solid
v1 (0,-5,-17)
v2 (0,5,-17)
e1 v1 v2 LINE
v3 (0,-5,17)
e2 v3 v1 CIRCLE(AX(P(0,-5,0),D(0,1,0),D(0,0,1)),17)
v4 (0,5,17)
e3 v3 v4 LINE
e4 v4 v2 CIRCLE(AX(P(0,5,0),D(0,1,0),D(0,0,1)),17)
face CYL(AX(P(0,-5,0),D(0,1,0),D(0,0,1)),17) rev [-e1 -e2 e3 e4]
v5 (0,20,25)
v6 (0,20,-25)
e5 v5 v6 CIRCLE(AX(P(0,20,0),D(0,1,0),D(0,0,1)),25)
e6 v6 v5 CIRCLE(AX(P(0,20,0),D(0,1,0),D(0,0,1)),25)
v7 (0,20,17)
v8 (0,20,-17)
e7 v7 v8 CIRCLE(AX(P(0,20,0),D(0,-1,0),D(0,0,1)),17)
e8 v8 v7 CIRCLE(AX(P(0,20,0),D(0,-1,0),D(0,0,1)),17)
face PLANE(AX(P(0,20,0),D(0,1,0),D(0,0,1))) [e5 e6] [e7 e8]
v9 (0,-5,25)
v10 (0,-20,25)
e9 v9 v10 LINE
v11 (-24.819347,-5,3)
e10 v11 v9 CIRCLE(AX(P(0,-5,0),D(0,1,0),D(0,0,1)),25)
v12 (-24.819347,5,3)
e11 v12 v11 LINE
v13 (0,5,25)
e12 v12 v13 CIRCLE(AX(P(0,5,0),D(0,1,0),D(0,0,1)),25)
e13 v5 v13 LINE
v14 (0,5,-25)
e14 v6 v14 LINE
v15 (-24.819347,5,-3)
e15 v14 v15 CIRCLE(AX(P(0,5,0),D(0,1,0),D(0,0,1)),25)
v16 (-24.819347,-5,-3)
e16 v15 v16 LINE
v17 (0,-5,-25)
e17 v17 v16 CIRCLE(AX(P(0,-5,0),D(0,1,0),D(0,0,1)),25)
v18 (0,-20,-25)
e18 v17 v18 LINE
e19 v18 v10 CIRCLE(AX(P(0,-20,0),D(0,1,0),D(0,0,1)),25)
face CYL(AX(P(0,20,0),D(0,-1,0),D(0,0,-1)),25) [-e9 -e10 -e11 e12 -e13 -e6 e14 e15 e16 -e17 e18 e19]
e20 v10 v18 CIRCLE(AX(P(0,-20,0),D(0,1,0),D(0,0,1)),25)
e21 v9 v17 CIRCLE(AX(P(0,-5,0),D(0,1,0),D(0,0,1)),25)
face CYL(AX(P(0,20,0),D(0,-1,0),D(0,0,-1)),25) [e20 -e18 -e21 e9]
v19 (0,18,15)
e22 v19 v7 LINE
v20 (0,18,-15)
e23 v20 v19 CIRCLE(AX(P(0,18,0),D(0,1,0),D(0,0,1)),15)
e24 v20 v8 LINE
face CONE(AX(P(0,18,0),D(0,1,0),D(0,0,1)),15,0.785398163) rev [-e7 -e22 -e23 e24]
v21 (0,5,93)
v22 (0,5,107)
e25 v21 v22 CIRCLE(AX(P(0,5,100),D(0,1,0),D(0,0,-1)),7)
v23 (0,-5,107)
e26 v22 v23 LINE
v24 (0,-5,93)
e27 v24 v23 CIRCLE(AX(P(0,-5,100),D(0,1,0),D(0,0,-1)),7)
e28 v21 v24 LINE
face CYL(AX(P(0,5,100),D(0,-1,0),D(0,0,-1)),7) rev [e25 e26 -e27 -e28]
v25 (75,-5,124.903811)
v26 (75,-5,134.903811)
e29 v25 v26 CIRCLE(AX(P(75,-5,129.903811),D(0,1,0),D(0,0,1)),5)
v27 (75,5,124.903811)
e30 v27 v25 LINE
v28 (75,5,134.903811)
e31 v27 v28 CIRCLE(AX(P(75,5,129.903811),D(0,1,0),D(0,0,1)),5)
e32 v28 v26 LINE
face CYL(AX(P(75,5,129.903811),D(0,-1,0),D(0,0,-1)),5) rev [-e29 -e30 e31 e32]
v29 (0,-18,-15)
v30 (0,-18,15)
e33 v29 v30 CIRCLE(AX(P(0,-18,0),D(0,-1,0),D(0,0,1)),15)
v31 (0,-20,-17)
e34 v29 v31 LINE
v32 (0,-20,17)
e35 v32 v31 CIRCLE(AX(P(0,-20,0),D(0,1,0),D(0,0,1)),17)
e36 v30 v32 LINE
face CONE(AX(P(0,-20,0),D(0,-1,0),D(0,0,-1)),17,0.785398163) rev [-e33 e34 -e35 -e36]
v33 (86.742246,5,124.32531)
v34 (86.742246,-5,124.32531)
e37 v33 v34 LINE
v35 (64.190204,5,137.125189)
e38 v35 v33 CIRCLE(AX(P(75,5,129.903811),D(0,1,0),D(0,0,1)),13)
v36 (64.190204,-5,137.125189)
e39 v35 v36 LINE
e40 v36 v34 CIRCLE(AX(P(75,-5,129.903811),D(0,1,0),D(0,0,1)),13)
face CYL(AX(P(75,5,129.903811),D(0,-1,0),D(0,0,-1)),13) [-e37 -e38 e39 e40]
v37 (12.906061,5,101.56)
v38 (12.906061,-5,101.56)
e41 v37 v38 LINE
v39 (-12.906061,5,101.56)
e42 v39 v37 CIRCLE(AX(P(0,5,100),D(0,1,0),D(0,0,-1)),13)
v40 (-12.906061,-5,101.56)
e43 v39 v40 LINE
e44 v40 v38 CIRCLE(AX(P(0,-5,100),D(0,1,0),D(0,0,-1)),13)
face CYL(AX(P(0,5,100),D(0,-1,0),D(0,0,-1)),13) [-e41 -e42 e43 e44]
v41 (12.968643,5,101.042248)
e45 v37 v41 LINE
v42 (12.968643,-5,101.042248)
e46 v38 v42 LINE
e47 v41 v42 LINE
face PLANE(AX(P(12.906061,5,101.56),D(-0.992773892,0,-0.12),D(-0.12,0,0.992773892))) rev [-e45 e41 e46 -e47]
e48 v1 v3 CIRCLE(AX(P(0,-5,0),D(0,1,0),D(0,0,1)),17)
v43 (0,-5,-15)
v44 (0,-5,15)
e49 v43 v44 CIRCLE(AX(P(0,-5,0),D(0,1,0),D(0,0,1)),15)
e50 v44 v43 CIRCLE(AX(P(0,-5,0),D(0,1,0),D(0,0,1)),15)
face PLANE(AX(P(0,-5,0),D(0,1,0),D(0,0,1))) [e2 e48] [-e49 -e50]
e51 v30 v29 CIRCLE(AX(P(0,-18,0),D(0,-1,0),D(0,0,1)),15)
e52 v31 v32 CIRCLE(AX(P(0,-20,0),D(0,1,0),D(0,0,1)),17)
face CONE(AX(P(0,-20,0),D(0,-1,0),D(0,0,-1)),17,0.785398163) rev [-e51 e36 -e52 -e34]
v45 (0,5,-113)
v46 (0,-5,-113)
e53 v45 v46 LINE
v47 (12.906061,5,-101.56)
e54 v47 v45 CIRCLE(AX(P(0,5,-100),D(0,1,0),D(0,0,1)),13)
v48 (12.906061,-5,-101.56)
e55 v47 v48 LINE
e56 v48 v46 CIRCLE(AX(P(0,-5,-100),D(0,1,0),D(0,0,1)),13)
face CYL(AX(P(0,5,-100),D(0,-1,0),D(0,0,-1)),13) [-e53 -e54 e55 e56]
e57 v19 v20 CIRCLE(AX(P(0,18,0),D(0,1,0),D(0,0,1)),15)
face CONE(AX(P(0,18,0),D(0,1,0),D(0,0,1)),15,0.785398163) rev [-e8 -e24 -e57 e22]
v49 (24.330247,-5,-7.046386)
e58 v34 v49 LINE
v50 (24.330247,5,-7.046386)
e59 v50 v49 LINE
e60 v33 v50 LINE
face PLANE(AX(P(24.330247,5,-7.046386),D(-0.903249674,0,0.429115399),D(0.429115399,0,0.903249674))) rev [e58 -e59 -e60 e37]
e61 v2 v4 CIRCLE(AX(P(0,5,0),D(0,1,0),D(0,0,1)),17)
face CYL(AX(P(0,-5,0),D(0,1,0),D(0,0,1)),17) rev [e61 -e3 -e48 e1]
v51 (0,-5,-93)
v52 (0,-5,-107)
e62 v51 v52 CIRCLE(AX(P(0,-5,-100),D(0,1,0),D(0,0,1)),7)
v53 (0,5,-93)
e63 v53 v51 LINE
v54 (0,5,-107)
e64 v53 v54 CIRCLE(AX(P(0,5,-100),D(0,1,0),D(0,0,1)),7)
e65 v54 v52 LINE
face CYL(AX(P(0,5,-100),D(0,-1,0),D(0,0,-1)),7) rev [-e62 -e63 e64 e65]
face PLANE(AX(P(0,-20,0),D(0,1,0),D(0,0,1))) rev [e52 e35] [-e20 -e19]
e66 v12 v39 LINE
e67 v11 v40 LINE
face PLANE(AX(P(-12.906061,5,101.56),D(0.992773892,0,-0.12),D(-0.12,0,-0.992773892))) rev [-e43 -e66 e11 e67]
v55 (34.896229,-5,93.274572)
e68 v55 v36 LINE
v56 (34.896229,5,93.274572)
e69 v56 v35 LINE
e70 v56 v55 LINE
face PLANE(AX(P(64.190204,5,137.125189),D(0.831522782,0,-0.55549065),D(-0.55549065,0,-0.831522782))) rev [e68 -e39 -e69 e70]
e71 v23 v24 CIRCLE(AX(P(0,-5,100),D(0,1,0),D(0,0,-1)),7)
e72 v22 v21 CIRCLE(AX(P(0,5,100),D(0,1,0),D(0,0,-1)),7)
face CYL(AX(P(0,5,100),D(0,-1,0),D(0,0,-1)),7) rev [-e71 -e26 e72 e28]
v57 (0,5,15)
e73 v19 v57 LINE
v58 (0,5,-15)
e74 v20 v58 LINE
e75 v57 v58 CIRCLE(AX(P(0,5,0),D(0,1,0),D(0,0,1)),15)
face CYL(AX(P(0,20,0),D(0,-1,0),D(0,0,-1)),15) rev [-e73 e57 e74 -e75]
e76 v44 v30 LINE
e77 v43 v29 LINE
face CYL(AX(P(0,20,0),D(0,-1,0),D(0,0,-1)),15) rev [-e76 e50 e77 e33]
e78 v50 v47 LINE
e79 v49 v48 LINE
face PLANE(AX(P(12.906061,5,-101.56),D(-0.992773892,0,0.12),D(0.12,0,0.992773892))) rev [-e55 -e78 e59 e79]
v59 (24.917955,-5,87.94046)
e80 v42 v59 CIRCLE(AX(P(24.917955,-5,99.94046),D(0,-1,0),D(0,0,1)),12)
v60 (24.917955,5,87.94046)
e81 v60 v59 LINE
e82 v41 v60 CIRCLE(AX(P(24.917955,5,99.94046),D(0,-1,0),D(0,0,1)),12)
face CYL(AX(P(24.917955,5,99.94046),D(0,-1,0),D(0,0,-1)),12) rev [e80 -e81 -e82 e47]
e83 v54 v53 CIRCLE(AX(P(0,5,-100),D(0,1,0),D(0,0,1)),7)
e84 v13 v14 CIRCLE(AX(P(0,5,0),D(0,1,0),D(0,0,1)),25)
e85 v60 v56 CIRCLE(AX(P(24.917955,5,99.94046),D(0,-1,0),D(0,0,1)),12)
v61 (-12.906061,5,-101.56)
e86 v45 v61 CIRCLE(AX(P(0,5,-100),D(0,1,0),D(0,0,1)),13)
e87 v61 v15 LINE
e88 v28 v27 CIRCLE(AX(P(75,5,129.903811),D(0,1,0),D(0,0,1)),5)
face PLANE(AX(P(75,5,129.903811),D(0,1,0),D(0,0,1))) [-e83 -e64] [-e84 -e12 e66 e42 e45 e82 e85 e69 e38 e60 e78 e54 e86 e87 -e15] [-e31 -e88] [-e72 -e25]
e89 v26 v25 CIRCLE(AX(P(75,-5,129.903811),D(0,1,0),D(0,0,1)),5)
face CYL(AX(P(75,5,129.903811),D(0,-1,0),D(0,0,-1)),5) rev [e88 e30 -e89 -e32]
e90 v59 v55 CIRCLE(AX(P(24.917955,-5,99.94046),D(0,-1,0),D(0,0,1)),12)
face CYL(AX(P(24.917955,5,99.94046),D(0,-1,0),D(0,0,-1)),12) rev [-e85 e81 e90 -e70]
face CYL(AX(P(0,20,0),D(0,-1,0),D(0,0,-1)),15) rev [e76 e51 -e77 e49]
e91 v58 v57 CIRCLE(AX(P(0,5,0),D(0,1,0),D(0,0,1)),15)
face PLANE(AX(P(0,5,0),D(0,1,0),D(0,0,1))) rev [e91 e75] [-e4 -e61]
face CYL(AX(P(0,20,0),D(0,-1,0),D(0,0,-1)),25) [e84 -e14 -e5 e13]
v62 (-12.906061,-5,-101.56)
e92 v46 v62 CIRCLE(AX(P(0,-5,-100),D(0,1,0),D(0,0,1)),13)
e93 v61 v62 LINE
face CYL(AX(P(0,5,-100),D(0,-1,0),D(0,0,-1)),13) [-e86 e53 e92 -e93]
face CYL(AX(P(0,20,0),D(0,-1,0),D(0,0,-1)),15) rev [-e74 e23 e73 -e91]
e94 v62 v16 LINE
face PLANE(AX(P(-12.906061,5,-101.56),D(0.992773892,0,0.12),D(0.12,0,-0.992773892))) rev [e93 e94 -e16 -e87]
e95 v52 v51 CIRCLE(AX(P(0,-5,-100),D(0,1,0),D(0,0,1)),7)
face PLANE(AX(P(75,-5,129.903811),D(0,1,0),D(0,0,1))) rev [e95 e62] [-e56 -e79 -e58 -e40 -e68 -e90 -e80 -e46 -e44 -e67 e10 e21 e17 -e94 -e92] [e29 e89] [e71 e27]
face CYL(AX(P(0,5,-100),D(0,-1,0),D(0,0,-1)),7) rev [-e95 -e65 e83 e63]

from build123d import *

# Parameters (mm, degrees)
SKETCH_1_R          = 25
SKETCH_1_R_2        = 15
EXTRUDE_1_DEPTH     = 20
SKETCH_2_R          = 15
SKETCH_2_R_2        = 7
SKETCH_2_R_3        = 5
EXTRUDE_2_DEPTH     = 5
CHAMFER_1_SIZE      = 2
SKETCH_3_R          = 17
CUT_EXTRUDE_1_DEPTH = 10


with BuildPart() as part:
    # 草图1 → 凸台-拉伸1 (new, symmetric)
    with BuildSketch(Plane(origin=(0, 0, 0), x_dir=(1, 0, 0), z_dir=(0, 1, 0))):
        with Locations(Location((0, 0, 0), (0, 0, 270))):
            Circle(SKETCH_1_R)
        with Locations(Location((0, 0, 0), (0, 0, 270))):
            Circle(SKETCH_1_R_2, mode=Mode.SUBTRACT)
    extrude(amount=EXTRUDE_1_DEPTH, both=True)

    # 草图2 → 凸台-拉伸2 (add, symmetric)
    with BuildSketch(Plane(origin=(0, 0, 0), x_dir=(1, 0, 0), z_dir=(0, 1, 0))):
        with BuildLine():
            Line((-12.906060592, 101.56), (-24.819347292, 3))
            ThreePointArc((-24.819347292, 3), (-25, 0), (-24.819347292, -3))
            Line((-24.819347292, -3), (-12.906060592, -101.56))
            ThreePointArc((-12.906060592, -101.56), (0, -113), (12.906060592, -101.56))
            Line((12.906060592, -101.56), (12.968643035, -101.042248202))
            ThreePointArc((12.968643035, -101.042248202), (20.91103038, -88.629202002), (34.896228635, -93.274572004))
            Line((34.896228635, -93.274572004), (64.19020383, -137.125189021))
            ThreePointArc((64.19020383, -137.125189021), (81.416898698, -141.209712173), (86.742245765, -124.325310375))
            Line((86.742245765, -124.325310375), (24.330246726, 7.046385599))
            Line((24.330246726, 7.046385599), (12.906060592, 101.56))
            ThreePointArc((12.906060592, 101.56), (0, 113), (-12.906060592, 101.56))
        make_face()
        with Locations(Location((0, 0, 0), (0, 0, 270))):
            Circle(SKETCH_2_R, mode=Mode.SUBTRACT)
        with Locations(Location((0, 100, 0), (0, 0, 270))):
            Circle(SKETCH_2_R_2, mode=Mode.SUBTRACT)
        with Locations(Location((0, -100, 0), (0, 0, 90))):
            Circle(SKETCH_2_R_2, mode=Mode.SUBTRACT)
        with Locations(Location((75, -129.903810568, 0), (0, 0, 270))):
            Circle(SKETCH_2_R_3, mode=Mode.SUBTRACT)
    extrude(amount=EXTRUDE_2_DEPTH, both=True)

    # 倒角1
    chamfer_1_edges = [part.edges().sort_by_distance(p)[0] for p in [
        (0, -20, -15),
        (0, 20, -15),
    ]]
    chamfer(chamfer_1_edges, length=CHAMFER_1_SIZE)

    # 草图3 → 切除-拉伸1 (cut)
    with BuildSketch(Plane(origin=(0, 5, 0), x_dir=(1, 0, 0), z_dir=(0, 1, 0))):
        with Locations(Location((0, 0, 0), (0, 0, 270))):
            Circle(SKETCH_3_R)
    extrude(amount=-CUT_EXTRUDE_1_DEPTH, mode=Mode.SUBTRACT)


solid = part.part
